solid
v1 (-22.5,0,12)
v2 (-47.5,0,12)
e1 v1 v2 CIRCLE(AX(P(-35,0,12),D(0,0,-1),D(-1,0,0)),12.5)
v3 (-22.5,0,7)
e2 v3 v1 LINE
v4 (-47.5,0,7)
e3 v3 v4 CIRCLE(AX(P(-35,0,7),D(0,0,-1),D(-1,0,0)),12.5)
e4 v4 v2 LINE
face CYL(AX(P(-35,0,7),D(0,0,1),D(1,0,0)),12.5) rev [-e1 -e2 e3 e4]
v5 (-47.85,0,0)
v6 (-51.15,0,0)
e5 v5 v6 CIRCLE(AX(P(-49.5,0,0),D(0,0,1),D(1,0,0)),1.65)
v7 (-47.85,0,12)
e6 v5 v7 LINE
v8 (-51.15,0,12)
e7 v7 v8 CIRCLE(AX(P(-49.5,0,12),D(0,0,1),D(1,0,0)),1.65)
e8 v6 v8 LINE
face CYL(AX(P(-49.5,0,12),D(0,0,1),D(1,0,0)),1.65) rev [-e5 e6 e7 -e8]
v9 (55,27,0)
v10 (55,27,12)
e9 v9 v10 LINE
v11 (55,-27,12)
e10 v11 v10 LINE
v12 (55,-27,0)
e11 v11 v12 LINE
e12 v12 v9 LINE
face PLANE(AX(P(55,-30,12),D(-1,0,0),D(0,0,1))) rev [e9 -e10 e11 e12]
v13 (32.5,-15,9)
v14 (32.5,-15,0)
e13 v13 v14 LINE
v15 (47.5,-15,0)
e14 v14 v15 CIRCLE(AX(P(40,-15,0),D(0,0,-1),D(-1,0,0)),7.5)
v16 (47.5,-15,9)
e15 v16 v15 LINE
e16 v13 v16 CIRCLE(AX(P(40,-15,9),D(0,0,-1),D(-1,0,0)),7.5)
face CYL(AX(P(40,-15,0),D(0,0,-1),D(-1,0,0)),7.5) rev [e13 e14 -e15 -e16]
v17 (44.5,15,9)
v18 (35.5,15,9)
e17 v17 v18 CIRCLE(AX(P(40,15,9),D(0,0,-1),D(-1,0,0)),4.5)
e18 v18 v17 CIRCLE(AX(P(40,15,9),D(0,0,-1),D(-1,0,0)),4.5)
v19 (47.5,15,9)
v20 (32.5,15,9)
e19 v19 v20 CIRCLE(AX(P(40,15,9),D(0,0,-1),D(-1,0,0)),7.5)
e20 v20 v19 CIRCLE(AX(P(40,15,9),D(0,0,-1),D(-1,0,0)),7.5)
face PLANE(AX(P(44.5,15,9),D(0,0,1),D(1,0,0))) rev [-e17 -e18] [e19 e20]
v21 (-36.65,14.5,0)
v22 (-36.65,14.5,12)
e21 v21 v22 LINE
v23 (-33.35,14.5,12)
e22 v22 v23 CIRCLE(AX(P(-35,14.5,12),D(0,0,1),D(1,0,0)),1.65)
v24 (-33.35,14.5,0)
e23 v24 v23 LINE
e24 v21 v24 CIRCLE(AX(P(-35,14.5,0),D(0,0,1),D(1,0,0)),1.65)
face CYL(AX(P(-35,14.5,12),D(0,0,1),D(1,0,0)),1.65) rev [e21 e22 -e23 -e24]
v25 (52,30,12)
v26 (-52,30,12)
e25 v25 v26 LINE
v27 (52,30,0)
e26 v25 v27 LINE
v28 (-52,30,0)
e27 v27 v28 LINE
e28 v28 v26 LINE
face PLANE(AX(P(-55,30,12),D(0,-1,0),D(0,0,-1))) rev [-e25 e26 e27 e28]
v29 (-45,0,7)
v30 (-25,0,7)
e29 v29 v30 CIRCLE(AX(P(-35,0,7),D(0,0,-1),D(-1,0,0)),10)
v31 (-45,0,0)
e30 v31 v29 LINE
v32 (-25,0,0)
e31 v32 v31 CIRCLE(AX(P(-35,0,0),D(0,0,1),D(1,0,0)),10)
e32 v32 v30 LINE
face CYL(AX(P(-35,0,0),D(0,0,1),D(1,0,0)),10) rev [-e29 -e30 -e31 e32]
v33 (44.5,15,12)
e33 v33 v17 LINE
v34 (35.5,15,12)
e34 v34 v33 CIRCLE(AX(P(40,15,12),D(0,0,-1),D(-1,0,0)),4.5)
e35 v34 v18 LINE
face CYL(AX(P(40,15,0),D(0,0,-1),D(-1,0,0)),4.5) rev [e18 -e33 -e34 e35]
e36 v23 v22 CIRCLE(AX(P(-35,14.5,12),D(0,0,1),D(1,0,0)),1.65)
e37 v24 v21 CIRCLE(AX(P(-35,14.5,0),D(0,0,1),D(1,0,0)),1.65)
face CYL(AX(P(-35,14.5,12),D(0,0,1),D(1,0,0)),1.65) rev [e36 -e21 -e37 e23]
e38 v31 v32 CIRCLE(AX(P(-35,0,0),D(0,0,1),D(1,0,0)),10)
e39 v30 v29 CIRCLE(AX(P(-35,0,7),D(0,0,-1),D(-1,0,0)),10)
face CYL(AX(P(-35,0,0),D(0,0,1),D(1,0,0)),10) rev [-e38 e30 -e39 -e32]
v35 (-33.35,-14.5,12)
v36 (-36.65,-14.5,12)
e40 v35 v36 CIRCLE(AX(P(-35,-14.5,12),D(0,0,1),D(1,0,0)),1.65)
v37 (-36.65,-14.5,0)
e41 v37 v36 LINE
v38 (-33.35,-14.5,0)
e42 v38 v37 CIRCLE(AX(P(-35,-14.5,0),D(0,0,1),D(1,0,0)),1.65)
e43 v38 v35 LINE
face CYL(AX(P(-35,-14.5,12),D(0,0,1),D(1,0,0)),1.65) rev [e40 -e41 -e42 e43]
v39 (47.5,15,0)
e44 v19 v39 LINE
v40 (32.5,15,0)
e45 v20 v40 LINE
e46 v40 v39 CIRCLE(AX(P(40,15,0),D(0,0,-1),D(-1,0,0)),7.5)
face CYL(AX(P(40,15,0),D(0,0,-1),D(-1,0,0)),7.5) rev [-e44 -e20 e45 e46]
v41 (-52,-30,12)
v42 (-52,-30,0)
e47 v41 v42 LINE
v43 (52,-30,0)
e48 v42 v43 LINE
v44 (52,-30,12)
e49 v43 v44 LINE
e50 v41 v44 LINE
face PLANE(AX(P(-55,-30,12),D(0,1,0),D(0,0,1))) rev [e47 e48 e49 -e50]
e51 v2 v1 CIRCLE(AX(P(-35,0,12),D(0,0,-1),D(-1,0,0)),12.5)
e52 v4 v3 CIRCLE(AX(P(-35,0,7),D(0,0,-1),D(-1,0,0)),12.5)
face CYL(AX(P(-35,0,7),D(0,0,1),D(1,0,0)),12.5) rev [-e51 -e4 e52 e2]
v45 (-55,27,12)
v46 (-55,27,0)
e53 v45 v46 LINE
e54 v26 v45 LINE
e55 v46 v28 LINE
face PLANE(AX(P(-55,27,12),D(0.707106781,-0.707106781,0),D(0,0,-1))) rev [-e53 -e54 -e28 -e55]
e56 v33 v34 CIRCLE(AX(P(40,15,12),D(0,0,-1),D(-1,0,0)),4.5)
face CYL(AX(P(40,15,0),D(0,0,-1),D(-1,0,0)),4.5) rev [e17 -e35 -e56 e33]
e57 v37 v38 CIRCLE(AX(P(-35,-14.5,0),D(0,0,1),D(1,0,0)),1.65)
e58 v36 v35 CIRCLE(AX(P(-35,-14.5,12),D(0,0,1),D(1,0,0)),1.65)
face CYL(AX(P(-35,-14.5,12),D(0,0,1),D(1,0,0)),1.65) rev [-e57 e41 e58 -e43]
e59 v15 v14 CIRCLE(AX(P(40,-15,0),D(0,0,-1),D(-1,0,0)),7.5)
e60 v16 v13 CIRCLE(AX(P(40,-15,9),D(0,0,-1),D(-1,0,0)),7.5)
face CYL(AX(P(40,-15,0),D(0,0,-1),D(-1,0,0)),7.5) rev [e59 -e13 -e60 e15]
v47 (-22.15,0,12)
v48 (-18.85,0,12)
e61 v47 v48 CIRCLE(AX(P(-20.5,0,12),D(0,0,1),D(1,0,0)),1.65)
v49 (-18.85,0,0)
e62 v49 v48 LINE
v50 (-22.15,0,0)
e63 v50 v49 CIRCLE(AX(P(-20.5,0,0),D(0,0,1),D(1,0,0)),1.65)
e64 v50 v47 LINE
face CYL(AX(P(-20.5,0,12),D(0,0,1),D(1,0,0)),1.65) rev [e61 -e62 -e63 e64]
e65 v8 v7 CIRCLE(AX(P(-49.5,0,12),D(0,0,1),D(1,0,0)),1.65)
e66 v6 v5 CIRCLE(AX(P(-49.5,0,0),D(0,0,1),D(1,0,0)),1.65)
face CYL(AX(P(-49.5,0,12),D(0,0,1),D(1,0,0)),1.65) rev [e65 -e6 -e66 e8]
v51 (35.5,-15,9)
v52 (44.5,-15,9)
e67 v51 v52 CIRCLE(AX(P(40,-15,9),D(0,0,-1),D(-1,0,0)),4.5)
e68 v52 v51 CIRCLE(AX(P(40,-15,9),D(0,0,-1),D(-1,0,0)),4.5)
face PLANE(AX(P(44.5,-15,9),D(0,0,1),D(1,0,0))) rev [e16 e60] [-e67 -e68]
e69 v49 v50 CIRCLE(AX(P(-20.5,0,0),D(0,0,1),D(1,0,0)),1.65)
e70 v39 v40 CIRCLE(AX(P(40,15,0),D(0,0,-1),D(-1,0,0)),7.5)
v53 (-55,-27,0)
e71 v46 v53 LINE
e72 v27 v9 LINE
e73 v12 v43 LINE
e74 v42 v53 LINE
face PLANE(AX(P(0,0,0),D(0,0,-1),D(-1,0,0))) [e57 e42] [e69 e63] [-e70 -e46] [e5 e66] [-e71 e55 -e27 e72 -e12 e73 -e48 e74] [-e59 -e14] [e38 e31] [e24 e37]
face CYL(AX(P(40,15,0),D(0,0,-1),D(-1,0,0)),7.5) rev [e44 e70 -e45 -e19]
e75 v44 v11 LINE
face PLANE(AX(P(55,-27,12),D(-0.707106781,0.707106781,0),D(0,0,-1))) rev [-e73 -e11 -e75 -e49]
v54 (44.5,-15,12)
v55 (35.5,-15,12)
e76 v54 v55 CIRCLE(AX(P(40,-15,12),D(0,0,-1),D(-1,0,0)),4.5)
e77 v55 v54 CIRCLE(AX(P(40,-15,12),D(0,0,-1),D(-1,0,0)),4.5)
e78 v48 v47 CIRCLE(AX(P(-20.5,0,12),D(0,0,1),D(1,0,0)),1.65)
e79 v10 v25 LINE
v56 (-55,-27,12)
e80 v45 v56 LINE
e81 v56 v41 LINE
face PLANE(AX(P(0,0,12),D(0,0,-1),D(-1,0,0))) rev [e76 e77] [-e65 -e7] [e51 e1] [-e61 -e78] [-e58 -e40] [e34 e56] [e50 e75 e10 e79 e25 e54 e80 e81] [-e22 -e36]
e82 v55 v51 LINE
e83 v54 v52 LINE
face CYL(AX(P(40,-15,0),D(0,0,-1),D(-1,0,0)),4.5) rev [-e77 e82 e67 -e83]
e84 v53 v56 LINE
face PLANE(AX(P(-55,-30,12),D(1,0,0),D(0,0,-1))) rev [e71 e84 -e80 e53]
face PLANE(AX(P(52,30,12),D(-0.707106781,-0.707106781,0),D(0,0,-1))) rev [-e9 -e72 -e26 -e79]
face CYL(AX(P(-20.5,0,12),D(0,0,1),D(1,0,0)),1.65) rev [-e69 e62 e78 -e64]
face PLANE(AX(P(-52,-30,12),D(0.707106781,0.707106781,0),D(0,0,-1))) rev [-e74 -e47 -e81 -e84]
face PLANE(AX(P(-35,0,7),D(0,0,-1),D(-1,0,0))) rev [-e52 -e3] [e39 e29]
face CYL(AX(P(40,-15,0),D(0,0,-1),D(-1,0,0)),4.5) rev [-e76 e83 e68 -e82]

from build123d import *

# Parameters (mm, degrees)
SKETCH1_W                                            = 110
SKETCH1_H                                            = 60
BOSS_EXTRUDE1_DEPTH                                  = 12
SKETCH2_R                                            = 12.5
CUT_EXTRUDE1_DEPTH                                   = 5
SKETCH3_R                                            = 10
CUT_EXTRUDE3_DEPTH                                   = 64.788713735
CHAMFER1_SIZE                                        = 3
M4_TAPPED_HOLE1_D                                    = 3.3
CBORE_FOR_M8_HEXAGON_SOCKET_HEAD_CAP_SCR_D           = 9
CBORE_FOR_M8_HEXAGON_SOCKET_HEAD_CAP_SCR_CBORE_D     = 15
CBORE_FOR_M8_HEXAGON_SOCKET_HEAD_CAP_SCR_CBORE_DEPTH = 9


with BuildPart() as part:
    # Sketch1 → Boss-Extrude1 (new body)
    with BuildSketch(Plane.XY):
        Rectangle(SKETCH1_W, SKETCH1_H)
    extrude(amount=BOSS_EXTRUDE1_DEPTH)

    # Sketch2 → Cut-Extrude1 (cut)
    with BuildSketch(Plane(origin=(0, 0, 12), x_dir=(-1, 0, 0), z_dir=(0, 0, -1))):
        with Locations((35, 0)):
            Circle(SKETCH2_R)
    extrude(amount=CUT_EXTRUDE1_DEPTH, mode=Mode.SUBTRACT)

    # Sketch3 → Cut-Extrude3 (cut, through all)
    with BuildSketch(Plane.XY.offset(12)):
        with Locations((-35, 0)):
            Circle(SKETCH3_R)
    extrude(amount=-CUT_EXTRUDE3_DEPTH, mode=Mode.SUBTRACT)

    # Chamfer1
    chamfer1_edges = [part.edges().sort_by_distance(p)[0] for p in [
        (55, -30, 6),
        (-55, -30, 6),
        (-55, 30, 6),
        (55, 30, 6),
    ]]
    chamfer(chamfer1_edges, length=CHAMFER1_SIZE)

    # M4 Tapped Hole1 (through all)
    with Locations(Plane.XY.offset(12)):
        with Locations((-35, 14.5), (-20.5, 0), (-49.5, 0), (-35, -14.5)):
            Hole(M4_TAPPED_HOLE1_D / 2)

    # CBORE for M8 Hexagon socket head cap screws1 (through all)
    with Locations(Plane(origin=(0, 0, 0), x_dir=(-1, 0, 0), z_dir=(0, 0, -1))):
        with Locations((-40, 15), (-40, -15)):
            CounterBoreHole(CBORE_FOR_M8_HEXAGON_SOCKET_HEAD_CAP_SCR_D / 2, CBORE_FOR_M8_HEXAGON_SOCKET_HEAD_CAP_SCR_CBORE_D / 2, CBORE_FOR_M8_HEXAGON_SOCKET_HEAD_CAP_SCR_CBORE_DEPTH)


solid = part.part
